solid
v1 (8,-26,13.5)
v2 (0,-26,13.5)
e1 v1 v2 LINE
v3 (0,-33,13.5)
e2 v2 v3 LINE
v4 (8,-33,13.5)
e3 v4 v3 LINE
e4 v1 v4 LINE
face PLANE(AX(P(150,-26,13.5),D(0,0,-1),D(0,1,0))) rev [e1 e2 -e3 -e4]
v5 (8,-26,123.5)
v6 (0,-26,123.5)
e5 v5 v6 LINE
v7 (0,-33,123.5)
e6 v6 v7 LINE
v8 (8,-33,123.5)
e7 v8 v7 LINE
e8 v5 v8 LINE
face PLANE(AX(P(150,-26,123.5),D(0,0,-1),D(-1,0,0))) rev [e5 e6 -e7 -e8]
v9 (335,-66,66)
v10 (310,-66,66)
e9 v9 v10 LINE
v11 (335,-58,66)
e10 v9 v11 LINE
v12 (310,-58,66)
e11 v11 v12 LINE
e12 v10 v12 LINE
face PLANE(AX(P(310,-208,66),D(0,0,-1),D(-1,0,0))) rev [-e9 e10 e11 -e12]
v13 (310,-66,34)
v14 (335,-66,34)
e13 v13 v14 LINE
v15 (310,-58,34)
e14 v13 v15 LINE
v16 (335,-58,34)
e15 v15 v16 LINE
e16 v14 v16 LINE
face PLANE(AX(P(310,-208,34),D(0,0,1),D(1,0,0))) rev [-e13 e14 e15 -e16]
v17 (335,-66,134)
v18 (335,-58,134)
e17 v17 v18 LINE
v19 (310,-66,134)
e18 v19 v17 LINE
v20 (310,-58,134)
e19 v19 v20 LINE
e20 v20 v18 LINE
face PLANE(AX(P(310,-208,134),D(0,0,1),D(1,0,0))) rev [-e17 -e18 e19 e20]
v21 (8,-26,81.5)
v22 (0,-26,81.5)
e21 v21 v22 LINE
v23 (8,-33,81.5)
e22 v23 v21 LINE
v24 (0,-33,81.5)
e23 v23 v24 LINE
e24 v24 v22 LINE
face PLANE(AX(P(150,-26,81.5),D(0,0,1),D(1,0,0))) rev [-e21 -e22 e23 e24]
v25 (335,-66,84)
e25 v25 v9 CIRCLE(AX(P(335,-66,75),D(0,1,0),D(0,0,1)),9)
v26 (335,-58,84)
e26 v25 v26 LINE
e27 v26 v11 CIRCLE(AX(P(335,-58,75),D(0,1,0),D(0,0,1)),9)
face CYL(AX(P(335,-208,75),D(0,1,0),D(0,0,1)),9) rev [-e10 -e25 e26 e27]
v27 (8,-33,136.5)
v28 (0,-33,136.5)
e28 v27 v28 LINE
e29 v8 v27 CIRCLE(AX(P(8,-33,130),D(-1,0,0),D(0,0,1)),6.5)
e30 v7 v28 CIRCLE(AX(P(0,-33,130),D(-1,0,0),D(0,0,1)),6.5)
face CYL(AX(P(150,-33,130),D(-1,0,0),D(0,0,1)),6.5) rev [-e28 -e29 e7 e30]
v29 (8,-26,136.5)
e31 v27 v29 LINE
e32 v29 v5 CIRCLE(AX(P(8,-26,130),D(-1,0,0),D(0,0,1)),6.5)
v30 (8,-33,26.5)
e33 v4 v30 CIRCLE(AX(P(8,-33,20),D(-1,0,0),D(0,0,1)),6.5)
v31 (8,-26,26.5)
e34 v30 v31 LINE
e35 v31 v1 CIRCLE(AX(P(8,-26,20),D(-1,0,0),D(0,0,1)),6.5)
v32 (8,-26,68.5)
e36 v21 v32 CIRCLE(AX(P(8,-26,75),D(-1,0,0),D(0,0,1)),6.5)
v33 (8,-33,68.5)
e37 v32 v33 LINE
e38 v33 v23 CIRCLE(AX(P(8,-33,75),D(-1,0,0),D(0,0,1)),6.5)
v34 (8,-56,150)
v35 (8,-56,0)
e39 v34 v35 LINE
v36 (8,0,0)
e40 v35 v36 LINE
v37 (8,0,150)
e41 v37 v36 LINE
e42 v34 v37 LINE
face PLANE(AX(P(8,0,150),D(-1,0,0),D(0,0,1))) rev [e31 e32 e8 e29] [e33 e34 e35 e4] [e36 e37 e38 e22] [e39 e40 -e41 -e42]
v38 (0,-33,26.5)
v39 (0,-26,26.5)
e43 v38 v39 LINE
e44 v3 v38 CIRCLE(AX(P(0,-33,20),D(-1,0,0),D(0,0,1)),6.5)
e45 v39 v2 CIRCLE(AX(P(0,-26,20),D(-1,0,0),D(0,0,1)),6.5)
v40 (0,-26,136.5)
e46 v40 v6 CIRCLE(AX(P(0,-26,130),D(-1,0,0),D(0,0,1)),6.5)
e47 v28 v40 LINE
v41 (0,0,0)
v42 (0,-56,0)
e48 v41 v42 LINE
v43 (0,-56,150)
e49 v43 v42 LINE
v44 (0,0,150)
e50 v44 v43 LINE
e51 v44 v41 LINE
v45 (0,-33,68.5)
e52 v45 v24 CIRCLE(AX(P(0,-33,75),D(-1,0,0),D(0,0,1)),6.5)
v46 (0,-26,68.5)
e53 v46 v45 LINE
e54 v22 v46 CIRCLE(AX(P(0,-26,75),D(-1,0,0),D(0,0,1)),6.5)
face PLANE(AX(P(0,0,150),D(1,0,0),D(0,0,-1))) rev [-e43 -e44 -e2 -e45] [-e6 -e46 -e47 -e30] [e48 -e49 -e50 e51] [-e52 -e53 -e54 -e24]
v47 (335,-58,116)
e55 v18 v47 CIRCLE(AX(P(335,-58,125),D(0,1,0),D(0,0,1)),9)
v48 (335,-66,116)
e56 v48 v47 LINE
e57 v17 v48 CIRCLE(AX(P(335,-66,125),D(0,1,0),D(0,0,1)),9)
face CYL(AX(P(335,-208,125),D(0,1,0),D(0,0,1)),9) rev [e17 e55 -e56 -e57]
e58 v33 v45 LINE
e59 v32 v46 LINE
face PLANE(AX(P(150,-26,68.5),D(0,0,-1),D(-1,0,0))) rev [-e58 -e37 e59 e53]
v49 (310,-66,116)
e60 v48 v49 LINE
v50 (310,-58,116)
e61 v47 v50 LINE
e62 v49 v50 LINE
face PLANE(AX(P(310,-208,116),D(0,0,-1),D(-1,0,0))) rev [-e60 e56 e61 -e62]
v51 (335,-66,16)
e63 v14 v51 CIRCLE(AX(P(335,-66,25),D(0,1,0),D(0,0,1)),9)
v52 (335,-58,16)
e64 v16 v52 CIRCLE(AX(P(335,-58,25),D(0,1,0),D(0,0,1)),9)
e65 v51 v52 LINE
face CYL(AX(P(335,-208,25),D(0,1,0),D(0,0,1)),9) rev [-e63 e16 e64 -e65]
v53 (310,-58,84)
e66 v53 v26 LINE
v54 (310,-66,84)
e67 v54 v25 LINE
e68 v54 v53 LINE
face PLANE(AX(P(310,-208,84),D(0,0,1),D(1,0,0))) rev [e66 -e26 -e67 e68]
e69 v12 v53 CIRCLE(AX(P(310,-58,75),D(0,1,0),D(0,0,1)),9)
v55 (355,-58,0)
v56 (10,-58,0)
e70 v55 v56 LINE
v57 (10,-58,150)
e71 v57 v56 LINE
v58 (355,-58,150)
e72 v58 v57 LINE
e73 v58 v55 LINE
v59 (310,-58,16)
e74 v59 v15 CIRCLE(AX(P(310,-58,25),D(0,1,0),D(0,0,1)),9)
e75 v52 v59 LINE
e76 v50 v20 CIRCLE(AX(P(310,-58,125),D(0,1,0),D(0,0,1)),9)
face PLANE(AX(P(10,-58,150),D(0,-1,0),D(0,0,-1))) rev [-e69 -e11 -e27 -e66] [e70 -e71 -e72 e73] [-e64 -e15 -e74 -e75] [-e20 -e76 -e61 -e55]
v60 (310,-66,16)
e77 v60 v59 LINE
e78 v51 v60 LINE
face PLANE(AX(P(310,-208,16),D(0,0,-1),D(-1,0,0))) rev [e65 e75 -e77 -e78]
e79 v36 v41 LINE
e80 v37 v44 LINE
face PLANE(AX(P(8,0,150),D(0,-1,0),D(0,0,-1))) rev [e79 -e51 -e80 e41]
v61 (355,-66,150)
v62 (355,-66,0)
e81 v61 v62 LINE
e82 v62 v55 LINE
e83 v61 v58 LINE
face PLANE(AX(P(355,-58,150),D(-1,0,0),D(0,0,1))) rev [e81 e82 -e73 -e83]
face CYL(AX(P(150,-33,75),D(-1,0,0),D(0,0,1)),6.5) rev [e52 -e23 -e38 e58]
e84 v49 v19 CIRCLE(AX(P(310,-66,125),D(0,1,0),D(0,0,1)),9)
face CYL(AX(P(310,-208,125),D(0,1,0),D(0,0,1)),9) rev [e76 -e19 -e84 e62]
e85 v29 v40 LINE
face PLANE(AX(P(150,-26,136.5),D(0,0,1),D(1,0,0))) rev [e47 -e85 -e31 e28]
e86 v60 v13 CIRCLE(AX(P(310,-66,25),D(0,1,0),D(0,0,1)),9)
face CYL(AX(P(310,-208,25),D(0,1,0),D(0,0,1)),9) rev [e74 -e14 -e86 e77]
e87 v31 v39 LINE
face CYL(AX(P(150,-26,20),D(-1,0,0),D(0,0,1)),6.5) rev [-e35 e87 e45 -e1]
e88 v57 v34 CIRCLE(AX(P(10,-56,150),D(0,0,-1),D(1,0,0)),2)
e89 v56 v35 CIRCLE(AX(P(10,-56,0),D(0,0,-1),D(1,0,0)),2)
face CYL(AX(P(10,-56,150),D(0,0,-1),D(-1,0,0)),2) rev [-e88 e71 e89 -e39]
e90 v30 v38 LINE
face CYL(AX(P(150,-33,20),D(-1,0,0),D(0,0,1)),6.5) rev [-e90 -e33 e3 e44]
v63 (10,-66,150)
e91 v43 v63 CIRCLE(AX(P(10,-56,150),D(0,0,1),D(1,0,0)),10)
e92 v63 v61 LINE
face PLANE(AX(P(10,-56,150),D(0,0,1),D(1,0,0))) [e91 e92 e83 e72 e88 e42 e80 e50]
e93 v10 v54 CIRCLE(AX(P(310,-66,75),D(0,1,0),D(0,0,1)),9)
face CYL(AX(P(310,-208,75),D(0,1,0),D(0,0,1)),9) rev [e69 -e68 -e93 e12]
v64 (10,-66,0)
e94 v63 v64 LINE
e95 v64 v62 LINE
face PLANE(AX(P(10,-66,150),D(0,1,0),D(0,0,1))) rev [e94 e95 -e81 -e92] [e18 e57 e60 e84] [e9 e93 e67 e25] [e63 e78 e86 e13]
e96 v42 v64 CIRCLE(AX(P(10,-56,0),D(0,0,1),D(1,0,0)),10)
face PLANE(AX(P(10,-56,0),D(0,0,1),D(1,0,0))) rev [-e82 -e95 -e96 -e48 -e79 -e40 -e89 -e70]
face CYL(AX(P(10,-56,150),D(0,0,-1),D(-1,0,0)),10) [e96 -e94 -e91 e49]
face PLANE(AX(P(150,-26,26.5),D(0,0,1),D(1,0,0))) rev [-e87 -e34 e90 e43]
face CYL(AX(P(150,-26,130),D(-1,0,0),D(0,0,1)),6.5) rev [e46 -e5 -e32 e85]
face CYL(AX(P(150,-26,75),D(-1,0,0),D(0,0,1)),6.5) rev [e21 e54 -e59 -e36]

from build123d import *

# Parameters (mm, degrees)
EXTRUDE_1_DEPTH     = 150
CUT_EXTRUDE_1_DEPTH = 150
CUT_EXTRUDE_2_DEPTH = 150


with BuildPart() as part:
    # 草图1 → 凸台-拉伸1 (new body)
    with BuildSketch(Plane.XY):
        with BuildLine():
            Line((0, 0), (0, -56))
            ThreePointArc((0, -56), (2.928932188, -63.071067812), (10, -66))
            Line((10, -66), (355, -66))
            Line((355, -66), (355, -58))
            Line((355, -58), (10, -58))
            ThreePointArc((10, -58), (8.585786438, -57.414213562), (8, -56))
            Line((8, -56), (8, 0))
            Line((8, 0), (0, 0))
        make_face()
    extrude(amount=EXTRUDE_1_DEPTH)

    # 草图2 → 切除-拉伸1 (cut)
    with BuildSketch(Plane.ZY):
        with BuildLine():
            Line((26.5, -26), (26.5, -33))
            ThreePointArc((26.5, -33), (20, -39.5), (13.5, -33))
            Line((13.5, -33), (13.5, -26))
            ThreePointArc((13.5, -26), (20, -19.5), (26.5, -26))
        make_face()
        with BuildLine():
            Line((81.5, -26), (81.5, -33))
            ThreePointArc((81.5, -33), (75, -39.5), (68.5, -33))
            Line((68.5, -33), (68.5, -26))
            ThreePointArc((68.5, -26), (75, -19.5), (81.5, -26))
        make_face()
        with BuildLine():
            Line((136.5, -26), (136.5, -33))
            ThreePointArc((136.5, -33), (130, -39.5), (123.5, -33))
            Line((123.5, -33), (123.5, -26))
            ThreePointArc((123.5, -26), (130, -19.5), (136.5, -26))
        make_face()
    extrude(amount=-CUT_EXTRUDE_1_DEPTH, mode=Mode.SUBTRACT)

    # 草图3 → 切除-拉伸2 (cut)
    with BuildSketch(Plane(origin=(0, -58, 0), x_dir=(1, 0, 0), z_dir=(0, 1, 0))):
        with BuildLine():
            Line((310, -16), (335, -16))
            ThreePointArc((335, -16), (344, -25), (335, -34))
            Line((335, -34), (310, -34))
            ThreePointArc((310, -34), (301, -25), (310, -16))
        make_face()
        with BuildLine():
            Line((310, -66), (335, -66))
            ThreePointArc((335, -66), (344, -75), (335, -84))
            Line((335, -84), (310, -84))
            ThreePointArc((310, -84), (301, -75), (310, -66))
        make_face()
        with BuildLine():
            Line((310, -116), (335, -116))
            ThreePointArc((335, -116), (344, -125), (335, -134))
            Line((335, -134), (310, -134))
            ThreePointArc((310, -134), (301, -125), (310, -116))
        make_face()
    extrude(amount=-CUT_EXTRUDE_2_DEPTH, mode=Mode.SUBTRACT)


solid = part.part
